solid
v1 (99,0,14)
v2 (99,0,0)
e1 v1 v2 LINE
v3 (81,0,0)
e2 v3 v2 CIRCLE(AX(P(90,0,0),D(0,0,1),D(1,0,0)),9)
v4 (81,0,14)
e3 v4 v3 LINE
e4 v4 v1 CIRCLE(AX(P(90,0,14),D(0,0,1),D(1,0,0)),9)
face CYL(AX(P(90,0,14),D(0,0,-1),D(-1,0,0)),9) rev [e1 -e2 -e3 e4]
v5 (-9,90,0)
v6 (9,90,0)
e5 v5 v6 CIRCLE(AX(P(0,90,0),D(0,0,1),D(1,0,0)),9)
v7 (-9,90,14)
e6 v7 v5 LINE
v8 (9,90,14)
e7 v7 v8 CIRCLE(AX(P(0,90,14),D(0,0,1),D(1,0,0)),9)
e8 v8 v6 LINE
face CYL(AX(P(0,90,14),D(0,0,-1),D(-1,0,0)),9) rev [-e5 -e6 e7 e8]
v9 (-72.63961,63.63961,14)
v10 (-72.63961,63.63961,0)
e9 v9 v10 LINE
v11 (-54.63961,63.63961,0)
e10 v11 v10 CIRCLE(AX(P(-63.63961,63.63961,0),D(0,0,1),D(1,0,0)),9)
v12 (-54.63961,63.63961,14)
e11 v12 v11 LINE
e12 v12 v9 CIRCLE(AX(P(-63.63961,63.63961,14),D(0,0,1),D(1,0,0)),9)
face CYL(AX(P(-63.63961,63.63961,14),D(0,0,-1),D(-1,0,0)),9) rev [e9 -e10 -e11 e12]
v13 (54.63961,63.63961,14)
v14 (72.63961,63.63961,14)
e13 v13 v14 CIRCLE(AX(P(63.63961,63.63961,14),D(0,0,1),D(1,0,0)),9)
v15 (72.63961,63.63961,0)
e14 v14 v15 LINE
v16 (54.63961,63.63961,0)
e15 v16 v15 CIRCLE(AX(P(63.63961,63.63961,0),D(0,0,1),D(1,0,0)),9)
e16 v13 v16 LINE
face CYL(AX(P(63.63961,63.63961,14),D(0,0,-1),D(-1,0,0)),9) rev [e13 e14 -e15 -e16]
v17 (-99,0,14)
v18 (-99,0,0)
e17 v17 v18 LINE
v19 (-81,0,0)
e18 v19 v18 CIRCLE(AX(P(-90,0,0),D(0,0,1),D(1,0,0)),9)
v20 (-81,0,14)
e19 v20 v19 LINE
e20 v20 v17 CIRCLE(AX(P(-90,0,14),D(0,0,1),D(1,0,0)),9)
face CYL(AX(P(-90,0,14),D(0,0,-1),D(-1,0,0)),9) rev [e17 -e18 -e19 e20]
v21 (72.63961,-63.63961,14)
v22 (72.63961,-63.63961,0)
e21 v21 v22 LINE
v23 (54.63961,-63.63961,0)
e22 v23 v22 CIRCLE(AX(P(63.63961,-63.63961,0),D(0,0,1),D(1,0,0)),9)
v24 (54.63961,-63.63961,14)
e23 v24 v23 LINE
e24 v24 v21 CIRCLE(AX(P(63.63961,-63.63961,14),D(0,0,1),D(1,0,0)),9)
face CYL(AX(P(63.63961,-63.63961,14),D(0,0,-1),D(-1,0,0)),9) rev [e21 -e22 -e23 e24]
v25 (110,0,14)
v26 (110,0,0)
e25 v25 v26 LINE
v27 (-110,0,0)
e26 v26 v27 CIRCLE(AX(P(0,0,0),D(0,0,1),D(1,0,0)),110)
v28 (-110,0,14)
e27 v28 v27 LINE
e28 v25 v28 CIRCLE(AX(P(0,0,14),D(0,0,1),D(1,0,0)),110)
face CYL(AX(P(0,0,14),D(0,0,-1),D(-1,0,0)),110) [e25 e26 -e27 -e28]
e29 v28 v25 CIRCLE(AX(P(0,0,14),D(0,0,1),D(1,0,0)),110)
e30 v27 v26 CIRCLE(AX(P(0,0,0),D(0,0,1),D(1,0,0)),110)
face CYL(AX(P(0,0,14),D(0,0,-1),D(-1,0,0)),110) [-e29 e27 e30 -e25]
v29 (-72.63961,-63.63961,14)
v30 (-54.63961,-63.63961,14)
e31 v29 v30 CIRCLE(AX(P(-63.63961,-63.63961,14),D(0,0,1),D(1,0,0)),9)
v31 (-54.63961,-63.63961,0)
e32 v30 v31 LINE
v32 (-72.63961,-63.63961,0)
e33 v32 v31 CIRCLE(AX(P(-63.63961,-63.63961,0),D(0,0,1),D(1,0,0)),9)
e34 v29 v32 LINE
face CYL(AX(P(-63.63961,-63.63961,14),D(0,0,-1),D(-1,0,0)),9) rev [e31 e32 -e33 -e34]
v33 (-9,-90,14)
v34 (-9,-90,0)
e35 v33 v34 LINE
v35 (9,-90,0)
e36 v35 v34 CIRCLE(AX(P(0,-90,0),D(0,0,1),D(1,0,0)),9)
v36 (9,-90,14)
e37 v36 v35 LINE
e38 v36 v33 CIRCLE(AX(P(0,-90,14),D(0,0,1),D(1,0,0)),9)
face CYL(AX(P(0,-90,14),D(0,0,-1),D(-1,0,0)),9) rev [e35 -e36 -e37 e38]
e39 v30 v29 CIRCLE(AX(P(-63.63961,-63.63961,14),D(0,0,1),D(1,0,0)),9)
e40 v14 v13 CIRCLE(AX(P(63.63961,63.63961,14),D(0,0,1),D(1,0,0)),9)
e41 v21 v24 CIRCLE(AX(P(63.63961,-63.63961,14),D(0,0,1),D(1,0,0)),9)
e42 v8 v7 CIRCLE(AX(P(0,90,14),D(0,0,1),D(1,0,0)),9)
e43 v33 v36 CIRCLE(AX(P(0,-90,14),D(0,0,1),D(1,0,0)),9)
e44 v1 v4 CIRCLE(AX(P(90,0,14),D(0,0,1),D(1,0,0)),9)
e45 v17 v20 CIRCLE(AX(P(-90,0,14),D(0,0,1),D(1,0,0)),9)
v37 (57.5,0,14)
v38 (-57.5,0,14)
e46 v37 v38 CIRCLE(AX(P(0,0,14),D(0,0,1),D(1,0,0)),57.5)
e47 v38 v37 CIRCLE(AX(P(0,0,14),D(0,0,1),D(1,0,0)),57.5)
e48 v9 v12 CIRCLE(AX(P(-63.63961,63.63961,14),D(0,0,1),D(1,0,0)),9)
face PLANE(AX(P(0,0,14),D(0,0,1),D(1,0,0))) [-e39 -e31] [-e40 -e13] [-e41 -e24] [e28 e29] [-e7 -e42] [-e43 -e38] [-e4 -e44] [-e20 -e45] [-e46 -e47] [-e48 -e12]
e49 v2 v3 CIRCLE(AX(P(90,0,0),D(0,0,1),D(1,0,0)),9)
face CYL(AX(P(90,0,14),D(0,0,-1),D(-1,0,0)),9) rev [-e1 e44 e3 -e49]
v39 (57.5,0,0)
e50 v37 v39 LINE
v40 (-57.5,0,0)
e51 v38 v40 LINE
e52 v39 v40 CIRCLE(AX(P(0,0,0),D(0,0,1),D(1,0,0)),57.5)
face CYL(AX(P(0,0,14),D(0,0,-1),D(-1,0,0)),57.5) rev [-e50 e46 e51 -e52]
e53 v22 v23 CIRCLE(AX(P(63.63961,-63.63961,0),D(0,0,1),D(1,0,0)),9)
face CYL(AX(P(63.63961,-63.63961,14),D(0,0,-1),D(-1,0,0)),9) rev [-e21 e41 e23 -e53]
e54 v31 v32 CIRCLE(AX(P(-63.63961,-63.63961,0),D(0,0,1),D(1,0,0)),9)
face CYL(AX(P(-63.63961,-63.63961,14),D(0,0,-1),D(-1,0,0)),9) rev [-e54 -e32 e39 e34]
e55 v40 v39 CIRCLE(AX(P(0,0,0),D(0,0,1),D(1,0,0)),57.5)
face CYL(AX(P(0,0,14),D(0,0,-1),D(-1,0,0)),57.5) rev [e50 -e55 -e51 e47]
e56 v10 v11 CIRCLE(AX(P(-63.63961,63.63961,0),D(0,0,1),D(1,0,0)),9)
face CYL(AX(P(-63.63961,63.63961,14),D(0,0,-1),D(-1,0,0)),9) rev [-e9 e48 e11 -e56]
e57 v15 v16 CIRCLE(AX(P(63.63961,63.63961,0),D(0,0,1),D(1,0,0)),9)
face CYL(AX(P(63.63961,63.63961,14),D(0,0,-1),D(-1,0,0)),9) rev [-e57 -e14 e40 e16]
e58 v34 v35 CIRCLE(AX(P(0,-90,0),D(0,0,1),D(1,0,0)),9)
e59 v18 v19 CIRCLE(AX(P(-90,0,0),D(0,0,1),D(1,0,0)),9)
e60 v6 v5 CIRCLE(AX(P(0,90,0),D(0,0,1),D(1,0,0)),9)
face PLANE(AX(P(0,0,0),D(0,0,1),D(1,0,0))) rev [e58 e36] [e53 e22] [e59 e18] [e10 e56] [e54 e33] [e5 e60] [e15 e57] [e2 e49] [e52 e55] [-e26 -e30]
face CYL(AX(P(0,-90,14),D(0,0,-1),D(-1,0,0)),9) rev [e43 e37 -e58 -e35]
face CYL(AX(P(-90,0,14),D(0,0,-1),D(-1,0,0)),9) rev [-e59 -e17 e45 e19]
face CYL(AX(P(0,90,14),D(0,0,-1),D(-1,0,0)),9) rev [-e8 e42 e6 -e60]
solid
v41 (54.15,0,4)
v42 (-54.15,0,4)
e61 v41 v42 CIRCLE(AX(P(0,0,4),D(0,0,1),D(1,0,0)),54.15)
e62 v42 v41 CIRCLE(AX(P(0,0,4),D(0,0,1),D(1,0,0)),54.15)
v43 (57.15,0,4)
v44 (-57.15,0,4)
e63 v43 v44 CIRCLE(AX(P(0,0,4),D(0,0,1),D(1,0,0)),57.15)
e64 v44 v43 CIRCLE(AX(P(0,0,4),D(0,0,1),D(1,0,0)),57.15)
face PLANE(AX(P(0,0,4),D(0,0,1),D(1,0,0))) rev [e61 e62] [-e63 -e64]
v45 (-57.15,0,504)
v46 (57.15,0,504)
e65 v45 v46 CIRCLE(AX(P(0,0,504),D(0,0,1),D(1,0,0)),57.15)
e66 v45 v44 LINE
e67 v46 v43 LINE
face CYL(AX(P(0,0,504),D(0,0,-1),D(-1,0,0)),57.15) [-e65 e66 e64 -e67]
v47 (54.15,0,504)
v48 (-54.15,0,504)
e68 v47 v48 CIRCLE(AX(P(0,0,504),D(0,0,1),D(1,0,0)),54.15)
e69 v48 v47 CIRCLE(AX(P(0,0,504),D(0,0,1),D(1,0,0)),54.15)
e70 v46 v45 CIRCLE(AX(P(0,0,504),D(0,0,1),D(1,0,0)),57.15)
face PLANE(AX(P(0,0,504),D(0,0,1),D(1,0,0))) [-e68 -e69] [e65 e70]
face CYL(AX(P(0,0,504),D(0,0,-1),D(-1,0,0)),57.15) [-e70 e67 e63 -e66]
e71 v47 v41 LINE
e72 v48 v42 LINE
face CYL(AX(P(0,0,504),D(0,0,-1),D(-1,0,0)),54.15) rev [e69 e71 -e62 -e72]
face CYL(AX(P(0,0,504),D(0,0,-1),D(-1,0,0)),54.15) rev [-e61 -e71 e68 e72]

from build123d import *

# Parameters (mm, degrees)
SKETCH1_R           = 110
SKETCH1_R_2         = 57.5
SKETCH1_R_3         = 9
BOSS_EXTRUDE1_DEPTH = 14
SKETCH2_R           = 57.15
SKETCH2_R_2         = 54.15
BOSS_EXTRUDE2_DEPTH = 500


with BuildPart() as part:
    # Sketch1 → Boss-Extrude1 (new body)
    with BuildSketch(Plane.XY):
        Circle(SKETCH1_R)
        Circle(SKETCH1_R_2, mode=Mode.SUBTRACT)
        with Locations((0, 90)):
            Circle(SKETCH1_R_3, mode=Mode.SUBTRACT)
        with Locations((63.639610307, 63.639610307)):
            Circle(SKETCH1_R_3, mode=Mode.SUBTRACT)
        with Locations((90, 0)):
            Circle(SKETCH1_R_3, mode=Mode.SUBTRACT)
        with Locations((63.639610307, -63.639610307)):
            Circle(SKETCH1_R_3, mode=Mode.SUBTRACT)
        with Locations((0, -90)):
            Circle(SKETCH1_R_3, mode=Mode.SUBTRACT)
        with Locations((-63.639610307, -63.639610307)):
            Circle(SKETCH1_R_3, mode=Mode.SUBTRACT)
        with Locations((-90, 0)):
            Circle(SKETCH1_R_3, mode=Mode.SUBTRACT)
        with Locations((-63.639610307, 63.639610307)):
            Circle(SKETCH1_R_3, mode=Mode.SUBTRACT)
    extrude(amount=BOSS_EXTRUDE1_DEPTH)


with BuildPart() as body_2:
    # Sketch2 → Boss-Extrude2 (new body)
    with BuildSketch(Plane.XY.offset(4)):
        Circle(SKETCH2_R)
        Circle(SKETCH2_R_2, mode=Mode.SUBTRACT)
    extrude(amount=BOSS_EXTRUDE2_DEPTH)


solid = Compound([part.part, body_2.part])
